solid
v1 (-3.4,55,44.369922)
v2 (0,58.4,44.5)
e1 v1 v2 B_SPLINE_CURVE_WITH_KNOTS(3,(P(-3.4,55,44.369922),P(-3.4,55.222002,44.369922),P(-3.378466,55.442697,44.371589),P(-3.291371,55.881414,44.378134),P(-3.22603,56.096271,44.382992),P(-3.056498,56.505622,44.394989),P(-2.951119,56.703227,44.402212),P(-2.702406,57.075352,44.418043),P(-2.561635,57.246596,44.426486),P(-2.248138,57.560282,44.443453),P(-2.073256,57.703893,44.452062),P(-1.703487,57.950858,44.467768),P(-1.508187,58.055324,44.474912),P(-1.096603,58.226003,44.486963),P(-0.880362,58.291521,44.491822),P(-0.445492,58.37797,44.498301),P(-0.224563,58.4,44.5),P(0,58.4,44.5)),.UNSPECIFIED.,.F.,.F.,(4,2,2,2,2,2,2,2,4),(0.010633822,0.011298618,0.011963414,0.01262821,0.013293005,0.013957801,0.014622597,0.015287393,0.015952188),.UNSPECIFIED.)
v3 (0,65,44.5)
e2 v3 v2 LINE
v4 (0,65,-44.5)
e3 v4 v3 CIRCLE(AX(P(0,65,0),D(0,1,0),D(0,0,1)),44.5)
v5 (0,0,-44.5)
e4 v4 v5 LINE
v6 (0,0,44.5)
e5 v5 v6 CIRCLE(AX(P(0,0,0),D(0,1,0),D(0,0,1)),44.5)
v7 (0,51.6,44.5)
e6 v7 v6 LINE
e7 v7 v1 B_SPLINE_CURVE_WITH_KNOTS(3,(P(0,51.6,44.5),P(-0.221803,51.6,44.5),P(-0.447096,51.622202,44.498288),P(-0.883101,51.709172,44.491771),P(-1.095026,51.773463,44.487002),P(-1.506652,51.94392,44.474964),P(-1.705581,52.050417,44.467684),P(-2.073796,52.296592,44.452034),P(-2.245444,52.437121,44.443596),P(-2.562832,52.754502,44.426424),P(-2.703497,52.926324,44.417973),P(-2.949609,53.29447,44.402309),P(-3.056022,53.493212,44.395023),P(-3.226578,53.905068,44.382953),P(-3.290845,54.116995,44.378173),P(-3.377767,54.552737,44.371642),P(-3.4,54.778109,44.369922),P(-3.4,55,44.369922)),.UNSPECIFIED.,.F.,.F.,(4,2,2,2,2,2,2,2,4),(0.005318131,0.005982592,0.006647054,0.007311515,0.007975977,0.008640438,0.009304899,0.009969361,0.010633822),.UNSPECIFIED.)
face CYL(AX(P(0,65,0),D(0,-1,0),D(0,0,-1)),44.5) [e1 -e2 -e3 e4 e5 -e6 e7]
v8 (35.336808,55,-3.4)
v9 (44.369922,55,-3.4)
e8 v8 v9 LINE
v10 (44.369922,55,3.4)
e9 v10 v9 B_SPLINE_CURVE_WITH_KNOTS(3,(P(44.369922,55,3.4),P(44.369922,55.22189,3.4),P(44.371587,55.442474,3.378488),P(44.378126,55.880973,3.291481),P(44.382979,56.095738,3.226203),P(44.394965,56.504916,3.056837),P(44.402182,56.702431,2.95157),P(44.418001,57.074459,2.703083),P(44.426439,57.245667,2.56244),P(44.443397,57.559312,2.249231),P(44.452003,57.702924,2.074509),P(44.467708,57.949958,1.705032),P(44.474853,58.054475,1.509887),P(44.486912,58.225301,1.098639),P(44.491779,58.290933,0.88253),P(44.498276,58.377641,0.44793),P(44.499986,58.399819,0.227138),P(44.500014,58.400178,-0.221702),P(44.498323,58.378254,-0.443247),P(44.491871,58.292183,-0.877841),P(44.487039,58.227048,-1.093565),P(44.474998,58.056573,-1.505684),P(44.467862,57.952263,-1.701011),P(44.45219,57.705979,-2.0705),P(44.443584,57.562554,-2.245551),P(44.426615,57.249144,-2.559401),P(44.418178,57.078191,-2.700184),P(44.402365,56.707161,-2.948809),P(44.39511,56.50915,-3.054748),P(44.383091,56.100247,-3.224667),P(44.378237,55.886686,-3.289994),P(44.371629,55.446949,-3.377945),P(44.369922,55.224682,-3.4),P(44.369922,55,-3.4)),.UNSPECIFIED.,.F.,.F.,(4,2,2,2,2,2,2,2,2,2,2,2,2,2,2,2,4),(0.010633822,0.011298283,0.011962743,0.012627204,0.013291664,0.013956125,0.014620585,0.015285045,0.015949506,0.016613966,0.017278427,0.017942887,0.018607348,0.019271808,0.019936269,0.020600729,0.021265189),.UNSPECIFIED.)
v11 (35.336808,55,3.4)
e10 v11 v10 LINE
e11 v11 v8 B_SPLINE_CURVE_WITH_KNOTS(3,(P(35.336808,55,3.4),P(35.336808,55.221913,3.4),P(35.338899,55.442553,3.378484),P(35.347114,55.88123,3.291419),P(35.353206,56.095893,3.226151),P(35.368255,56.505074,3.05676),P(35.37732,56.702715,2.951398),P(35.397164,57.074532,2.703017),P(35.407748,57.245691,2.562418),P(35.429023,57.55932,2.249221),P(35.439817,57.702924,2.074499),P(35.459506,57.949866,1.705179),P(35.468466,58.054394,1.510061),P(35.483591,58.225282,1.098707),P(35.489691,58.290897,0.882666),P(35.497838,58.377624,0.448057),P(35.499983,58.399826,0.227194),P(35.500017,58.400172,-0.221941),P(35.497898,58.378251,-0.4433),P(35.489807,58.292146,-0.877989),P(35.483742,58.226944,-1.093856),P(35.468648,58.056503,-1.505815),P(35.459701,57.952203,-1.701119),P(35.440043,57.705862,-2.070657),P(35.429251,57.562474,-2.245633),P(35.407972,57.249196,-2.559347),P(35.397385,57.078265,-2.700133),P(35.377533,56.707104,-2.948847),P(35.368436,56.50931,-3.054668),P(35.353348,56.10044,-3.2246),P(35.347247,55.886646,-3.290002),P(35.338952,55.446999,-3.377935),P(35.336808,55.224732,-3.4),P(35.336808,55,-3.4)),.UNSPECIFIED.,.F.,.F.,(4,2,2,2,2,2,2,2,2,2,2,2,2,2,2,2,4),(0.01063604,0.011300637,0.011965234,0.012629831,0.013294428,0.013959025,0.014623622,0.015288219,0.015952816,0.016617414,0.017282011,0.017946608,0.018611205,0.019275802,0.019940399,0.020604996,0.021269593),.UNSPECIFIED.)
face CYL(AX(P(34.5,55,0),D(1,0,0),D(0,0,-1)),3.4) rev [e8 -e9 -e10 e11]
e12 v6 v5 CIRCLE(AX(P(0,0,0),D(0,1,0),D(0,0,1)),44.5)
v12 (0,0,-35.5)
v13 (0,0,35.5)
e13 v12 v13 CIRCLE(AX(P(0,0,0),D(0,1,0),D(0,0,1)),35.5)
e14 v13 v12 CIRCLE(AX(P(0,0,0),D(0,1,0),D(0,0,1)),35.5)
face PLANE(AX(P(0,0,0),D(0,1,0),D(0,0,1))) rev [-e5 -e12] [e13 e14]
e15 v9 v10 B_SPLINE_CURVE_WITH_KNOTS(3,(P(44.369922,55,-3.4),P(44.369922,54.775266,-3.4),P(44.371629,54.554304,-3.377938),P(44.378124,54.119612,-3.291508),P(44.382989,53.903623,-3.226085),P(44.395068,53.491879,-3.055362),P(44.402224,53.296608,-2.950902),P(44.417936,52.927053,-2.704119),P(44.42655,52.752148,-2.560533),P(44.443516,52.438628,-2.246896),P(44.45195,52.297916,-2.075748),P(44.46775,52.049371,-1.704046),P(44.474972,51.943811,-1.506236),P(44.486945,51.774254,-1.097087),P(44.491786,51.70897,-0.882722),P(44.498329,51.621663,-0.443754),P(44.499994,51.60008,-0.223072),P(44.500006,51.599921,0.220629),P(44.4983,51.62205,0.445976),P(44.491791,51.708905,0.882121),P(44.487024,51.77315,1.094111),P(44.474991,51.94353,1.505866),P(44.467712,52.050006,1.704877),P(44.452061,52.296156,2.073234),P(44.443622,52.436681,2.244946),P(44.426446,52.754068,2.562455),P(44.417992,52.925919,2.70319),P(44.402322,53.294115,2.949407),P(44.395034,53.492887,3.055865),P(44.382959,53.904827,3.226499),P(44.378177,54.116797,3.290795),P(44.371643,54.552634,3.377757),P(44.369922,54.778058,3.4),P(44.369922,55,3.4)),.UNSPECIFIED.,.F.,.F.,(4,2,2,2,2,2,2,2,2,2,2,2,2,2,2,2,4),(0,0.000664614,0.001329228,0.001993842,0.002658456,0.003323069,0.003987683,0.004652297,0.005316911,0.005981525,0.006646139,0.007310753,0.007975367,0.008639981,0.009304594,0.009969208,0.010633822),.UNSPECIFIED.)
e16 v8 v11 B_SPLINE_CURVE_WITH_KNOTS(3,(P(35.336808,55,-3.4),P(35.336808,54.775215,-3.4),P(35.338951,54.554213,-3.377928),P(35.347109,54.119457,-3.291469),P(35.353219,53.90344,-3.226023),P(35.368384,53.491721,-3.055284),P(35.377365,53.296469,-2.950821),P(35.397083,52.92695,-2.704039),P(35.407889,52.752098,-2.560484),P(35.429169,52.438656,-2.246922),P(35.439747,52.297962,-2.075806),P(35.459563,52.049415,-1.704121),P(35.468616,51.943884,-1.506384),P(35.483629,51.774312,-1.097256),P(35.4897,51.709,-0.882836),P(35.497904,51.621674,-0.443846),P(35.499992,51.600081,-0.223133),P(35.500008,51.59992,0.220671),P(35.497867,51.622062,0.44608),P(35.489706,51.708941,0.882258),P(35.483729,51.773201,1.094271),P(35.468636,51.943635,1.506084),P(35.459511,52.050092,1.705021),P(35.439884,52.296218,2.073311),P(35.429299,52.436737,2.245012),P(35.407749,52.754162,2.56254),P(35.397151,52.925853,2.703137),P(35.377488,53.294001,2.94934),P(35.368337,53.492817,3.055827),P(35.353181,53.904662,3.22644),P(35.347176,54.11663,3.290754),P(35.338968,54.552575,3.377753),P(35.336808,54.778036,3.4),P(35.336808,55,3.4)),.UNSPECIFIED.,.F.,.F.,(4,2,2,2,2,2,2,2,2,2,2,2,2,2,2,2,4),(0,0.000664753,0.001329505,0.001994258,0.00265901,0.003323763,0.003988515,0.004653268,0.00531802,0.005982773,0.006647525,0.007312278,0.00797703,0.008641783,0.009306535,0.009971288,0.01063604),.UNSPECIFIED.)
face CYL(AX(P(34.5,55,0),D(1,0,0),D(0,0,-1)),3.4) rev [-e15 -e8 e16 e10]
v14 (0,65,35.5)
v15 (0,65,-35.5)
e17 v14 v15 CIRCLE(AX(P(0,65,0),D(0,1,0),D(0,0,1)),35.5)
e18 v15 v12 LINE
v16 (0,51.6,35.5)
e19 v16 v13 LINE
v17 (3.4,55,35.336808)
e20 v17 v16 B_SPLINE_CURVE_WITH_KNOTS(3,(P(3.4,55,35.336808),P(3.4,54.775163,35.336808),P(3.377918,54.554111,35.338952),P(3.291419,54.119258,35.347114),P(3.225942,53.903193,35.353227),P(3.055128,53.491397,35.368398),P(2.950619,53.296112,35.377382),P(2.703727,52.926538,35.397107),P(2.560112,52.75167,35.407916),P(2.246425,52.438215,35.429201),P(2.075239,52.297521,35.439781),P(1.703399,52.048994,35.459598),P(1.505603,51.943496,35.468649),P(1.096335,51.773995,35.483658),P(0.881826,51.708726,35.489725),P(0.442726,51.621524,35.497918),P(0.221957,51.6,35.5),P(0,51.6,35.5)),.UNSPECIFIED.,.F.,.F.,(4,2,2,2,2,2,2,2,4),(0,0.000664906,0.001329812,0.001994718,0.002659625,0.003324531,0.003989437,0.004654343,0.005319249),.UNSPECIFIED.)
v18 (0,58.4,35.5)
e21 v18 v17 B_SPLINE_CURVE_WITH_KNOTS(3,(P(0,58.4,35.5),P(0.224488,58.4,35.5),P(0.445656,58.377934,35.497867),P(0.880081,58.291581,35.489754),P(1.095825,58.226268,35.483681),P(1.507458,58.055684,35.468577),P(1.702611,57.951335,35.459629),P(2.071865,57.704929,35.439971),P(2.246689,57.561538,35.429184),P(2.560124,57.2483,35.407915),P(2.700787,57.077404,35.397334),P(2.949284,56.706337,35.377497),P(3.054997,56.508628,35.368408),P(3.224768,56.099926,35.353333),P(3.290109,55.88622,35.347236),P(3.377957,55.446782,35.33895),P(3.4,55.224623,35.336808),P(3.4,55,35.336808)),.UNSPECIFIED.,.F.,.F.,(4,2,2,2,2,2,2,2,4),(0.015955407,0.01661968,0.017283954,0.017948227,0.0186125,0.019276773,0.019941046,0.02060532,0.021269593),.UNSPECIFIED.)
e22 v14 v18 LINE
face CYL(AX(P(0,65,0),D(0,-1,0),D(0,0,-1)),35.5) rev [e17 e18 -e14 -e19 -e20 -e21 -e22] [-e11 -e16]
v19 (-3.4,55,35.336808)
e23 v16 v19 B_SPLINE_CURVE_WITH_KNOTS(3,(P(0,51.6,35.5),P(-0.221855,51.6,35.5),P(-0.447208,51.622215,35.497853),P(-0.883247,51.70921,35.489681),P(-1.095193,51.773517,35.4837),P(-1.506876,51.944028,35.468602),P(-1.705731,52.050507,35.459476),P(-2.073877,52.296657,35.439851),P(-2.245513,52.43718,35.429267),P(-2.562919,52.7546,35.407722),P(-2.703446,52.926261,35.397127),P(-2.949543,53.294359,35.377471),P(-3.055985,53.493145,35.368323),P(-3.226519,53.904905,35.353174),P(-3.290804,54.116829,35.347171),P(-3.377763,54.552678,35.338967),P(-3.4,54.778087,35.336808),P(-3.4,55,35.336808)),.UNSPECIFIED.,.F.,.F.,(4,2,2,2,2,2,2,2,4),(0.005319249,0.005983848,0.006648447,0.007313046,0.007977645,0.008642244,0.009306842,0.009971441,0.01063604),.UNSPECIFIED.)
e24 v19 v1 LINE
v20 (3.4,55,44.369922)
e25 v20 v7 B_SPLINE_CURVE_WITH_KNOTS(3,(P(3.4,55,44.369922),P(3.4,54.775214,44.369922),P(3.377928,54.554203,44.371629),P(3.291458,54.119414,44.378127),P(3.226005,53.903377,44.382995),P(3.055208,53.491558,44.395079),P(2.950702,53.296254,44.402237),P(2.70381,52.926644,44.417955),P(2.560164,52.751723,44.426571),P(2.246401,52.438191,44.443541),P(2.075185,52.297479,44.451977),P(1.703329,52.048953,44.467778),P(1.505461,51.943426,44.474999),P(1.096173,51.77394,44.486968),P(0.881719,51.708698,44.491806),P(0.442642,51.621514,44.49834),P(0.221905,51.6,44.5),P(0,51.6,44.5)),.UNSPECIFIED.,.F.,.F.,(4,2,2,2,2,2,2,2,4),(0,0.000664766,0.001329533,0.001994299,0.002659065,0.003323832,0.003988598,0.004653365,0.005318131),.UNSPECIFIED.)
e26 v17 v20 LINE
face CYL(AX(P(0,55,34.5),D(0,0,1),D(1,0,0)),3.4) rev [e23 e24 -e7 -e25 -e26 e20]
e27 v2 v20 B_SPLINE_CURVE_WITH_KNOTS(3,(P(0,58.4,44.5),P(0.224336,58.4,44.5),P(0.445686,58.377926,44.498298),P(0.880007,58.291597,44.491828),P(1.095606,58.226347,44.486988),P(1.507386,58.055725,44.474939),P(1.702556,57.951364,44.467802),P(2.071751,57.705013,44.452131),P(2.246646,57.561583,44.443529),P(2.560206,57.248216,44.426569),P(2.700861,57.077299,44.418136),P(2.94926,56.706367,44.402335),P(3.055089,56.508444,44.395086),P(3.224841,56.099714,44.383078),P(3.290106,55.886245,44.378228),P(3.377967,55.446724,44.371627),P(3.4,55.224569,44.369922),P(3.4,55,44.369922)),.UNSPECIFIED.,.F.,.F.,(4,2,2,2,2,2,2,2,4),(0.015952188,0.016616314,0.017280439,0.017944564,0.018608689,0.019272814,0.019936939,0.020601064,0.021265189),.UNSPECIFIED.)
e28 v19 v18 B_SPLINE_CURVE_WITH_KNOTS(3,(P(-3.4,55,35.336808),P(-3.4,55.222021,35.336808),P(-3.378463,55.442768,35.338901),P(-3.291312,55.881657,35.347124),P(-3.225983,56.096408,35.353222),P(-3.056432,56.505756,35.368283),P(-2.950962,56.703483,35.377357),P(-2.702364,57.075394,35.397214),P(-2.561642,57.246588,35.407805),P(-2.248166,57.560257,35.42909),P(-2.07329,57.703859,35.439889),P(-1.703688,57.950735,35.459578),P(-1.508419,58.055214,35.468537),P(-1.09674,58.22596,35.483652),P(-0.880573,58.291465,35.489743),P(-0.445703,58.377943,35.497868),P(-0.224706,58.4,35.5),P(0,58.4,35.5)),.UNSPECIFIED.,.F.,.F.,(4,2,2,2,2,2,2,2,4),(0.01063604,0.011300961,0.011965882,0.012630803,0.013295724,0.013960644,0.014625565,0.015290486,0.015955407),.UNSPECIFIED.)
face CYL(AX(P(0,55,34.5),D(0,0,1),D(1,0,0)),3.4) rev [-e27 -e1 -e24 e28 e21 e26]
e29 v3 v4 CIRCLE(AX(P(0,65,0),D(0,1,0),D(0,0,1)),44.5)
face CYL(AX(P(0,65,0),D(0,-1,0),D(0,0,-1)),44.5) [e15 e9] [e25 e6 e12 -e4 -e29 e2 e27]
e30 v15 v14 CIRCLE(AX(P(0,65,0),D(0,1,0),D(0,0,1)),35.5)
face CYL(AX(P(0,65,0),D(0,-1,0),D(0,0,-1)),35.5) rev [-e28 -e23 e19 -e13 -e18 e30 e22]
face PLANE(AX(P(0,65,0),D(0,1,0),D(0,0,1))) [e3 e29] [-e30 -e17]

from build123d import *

# Parameters (mm, degrees)
SKETCH1_R           = 44.5
SKETCH1_R_2         = 35.5
BOSS_EXTRUDE1_DEPTH = 65
SKETCH3_R           = 3.4
CUT_EXTRUDE1_DEPTH  = 10
SKETCH4_R           = 3.4
CUT_EXTRUDE2_DEPTH  = 10


with BuildPart() as part:
    # Sketch1 → Boss-Extrude1 (new body)
    with BuildSketch(Plane(origin=(0, 0, 0), x_dir=(1, 0, 0), z_dir=(0, 1, 0))):
        with Locations(Location((0, 0, 0), (0, 0, 270))):
            Circle(SKETCH1_R)
        with Locations(Location((0, 0, 0), (0, 0, 270))):
            Circle(SKETCH1_R_2, mode=Mode.SUBTRACT)
    extrude(amount=BOSS_EXTRUDE1_DEPTH)

    # Sketch3 → Cut-Extrude1 (cut)
    with BuildSketch(Plane(origin=(44.5, 0, 0), x_dir=(0, 0, -1), z_dir=(1, 0, 0))):
        with Locations((0, 55)):
            Circle(SKETCH3_R)
    extrude(amount=-CUT_EXTRUDE1_DEPTH, mode=Mode.SUBTRACT)

    # Sketch4 → Cut-Extrude2 (cut)
    with BuildSketch(Plane.XY.offset(44.5)):
        with Locations((0, 55)):
            Circle(SKETCH4_R)
    extrude(amount=-CUT_EXTRUDE2_DEPTH, mode=Mode.SUBTRACT)


solid = part.part
